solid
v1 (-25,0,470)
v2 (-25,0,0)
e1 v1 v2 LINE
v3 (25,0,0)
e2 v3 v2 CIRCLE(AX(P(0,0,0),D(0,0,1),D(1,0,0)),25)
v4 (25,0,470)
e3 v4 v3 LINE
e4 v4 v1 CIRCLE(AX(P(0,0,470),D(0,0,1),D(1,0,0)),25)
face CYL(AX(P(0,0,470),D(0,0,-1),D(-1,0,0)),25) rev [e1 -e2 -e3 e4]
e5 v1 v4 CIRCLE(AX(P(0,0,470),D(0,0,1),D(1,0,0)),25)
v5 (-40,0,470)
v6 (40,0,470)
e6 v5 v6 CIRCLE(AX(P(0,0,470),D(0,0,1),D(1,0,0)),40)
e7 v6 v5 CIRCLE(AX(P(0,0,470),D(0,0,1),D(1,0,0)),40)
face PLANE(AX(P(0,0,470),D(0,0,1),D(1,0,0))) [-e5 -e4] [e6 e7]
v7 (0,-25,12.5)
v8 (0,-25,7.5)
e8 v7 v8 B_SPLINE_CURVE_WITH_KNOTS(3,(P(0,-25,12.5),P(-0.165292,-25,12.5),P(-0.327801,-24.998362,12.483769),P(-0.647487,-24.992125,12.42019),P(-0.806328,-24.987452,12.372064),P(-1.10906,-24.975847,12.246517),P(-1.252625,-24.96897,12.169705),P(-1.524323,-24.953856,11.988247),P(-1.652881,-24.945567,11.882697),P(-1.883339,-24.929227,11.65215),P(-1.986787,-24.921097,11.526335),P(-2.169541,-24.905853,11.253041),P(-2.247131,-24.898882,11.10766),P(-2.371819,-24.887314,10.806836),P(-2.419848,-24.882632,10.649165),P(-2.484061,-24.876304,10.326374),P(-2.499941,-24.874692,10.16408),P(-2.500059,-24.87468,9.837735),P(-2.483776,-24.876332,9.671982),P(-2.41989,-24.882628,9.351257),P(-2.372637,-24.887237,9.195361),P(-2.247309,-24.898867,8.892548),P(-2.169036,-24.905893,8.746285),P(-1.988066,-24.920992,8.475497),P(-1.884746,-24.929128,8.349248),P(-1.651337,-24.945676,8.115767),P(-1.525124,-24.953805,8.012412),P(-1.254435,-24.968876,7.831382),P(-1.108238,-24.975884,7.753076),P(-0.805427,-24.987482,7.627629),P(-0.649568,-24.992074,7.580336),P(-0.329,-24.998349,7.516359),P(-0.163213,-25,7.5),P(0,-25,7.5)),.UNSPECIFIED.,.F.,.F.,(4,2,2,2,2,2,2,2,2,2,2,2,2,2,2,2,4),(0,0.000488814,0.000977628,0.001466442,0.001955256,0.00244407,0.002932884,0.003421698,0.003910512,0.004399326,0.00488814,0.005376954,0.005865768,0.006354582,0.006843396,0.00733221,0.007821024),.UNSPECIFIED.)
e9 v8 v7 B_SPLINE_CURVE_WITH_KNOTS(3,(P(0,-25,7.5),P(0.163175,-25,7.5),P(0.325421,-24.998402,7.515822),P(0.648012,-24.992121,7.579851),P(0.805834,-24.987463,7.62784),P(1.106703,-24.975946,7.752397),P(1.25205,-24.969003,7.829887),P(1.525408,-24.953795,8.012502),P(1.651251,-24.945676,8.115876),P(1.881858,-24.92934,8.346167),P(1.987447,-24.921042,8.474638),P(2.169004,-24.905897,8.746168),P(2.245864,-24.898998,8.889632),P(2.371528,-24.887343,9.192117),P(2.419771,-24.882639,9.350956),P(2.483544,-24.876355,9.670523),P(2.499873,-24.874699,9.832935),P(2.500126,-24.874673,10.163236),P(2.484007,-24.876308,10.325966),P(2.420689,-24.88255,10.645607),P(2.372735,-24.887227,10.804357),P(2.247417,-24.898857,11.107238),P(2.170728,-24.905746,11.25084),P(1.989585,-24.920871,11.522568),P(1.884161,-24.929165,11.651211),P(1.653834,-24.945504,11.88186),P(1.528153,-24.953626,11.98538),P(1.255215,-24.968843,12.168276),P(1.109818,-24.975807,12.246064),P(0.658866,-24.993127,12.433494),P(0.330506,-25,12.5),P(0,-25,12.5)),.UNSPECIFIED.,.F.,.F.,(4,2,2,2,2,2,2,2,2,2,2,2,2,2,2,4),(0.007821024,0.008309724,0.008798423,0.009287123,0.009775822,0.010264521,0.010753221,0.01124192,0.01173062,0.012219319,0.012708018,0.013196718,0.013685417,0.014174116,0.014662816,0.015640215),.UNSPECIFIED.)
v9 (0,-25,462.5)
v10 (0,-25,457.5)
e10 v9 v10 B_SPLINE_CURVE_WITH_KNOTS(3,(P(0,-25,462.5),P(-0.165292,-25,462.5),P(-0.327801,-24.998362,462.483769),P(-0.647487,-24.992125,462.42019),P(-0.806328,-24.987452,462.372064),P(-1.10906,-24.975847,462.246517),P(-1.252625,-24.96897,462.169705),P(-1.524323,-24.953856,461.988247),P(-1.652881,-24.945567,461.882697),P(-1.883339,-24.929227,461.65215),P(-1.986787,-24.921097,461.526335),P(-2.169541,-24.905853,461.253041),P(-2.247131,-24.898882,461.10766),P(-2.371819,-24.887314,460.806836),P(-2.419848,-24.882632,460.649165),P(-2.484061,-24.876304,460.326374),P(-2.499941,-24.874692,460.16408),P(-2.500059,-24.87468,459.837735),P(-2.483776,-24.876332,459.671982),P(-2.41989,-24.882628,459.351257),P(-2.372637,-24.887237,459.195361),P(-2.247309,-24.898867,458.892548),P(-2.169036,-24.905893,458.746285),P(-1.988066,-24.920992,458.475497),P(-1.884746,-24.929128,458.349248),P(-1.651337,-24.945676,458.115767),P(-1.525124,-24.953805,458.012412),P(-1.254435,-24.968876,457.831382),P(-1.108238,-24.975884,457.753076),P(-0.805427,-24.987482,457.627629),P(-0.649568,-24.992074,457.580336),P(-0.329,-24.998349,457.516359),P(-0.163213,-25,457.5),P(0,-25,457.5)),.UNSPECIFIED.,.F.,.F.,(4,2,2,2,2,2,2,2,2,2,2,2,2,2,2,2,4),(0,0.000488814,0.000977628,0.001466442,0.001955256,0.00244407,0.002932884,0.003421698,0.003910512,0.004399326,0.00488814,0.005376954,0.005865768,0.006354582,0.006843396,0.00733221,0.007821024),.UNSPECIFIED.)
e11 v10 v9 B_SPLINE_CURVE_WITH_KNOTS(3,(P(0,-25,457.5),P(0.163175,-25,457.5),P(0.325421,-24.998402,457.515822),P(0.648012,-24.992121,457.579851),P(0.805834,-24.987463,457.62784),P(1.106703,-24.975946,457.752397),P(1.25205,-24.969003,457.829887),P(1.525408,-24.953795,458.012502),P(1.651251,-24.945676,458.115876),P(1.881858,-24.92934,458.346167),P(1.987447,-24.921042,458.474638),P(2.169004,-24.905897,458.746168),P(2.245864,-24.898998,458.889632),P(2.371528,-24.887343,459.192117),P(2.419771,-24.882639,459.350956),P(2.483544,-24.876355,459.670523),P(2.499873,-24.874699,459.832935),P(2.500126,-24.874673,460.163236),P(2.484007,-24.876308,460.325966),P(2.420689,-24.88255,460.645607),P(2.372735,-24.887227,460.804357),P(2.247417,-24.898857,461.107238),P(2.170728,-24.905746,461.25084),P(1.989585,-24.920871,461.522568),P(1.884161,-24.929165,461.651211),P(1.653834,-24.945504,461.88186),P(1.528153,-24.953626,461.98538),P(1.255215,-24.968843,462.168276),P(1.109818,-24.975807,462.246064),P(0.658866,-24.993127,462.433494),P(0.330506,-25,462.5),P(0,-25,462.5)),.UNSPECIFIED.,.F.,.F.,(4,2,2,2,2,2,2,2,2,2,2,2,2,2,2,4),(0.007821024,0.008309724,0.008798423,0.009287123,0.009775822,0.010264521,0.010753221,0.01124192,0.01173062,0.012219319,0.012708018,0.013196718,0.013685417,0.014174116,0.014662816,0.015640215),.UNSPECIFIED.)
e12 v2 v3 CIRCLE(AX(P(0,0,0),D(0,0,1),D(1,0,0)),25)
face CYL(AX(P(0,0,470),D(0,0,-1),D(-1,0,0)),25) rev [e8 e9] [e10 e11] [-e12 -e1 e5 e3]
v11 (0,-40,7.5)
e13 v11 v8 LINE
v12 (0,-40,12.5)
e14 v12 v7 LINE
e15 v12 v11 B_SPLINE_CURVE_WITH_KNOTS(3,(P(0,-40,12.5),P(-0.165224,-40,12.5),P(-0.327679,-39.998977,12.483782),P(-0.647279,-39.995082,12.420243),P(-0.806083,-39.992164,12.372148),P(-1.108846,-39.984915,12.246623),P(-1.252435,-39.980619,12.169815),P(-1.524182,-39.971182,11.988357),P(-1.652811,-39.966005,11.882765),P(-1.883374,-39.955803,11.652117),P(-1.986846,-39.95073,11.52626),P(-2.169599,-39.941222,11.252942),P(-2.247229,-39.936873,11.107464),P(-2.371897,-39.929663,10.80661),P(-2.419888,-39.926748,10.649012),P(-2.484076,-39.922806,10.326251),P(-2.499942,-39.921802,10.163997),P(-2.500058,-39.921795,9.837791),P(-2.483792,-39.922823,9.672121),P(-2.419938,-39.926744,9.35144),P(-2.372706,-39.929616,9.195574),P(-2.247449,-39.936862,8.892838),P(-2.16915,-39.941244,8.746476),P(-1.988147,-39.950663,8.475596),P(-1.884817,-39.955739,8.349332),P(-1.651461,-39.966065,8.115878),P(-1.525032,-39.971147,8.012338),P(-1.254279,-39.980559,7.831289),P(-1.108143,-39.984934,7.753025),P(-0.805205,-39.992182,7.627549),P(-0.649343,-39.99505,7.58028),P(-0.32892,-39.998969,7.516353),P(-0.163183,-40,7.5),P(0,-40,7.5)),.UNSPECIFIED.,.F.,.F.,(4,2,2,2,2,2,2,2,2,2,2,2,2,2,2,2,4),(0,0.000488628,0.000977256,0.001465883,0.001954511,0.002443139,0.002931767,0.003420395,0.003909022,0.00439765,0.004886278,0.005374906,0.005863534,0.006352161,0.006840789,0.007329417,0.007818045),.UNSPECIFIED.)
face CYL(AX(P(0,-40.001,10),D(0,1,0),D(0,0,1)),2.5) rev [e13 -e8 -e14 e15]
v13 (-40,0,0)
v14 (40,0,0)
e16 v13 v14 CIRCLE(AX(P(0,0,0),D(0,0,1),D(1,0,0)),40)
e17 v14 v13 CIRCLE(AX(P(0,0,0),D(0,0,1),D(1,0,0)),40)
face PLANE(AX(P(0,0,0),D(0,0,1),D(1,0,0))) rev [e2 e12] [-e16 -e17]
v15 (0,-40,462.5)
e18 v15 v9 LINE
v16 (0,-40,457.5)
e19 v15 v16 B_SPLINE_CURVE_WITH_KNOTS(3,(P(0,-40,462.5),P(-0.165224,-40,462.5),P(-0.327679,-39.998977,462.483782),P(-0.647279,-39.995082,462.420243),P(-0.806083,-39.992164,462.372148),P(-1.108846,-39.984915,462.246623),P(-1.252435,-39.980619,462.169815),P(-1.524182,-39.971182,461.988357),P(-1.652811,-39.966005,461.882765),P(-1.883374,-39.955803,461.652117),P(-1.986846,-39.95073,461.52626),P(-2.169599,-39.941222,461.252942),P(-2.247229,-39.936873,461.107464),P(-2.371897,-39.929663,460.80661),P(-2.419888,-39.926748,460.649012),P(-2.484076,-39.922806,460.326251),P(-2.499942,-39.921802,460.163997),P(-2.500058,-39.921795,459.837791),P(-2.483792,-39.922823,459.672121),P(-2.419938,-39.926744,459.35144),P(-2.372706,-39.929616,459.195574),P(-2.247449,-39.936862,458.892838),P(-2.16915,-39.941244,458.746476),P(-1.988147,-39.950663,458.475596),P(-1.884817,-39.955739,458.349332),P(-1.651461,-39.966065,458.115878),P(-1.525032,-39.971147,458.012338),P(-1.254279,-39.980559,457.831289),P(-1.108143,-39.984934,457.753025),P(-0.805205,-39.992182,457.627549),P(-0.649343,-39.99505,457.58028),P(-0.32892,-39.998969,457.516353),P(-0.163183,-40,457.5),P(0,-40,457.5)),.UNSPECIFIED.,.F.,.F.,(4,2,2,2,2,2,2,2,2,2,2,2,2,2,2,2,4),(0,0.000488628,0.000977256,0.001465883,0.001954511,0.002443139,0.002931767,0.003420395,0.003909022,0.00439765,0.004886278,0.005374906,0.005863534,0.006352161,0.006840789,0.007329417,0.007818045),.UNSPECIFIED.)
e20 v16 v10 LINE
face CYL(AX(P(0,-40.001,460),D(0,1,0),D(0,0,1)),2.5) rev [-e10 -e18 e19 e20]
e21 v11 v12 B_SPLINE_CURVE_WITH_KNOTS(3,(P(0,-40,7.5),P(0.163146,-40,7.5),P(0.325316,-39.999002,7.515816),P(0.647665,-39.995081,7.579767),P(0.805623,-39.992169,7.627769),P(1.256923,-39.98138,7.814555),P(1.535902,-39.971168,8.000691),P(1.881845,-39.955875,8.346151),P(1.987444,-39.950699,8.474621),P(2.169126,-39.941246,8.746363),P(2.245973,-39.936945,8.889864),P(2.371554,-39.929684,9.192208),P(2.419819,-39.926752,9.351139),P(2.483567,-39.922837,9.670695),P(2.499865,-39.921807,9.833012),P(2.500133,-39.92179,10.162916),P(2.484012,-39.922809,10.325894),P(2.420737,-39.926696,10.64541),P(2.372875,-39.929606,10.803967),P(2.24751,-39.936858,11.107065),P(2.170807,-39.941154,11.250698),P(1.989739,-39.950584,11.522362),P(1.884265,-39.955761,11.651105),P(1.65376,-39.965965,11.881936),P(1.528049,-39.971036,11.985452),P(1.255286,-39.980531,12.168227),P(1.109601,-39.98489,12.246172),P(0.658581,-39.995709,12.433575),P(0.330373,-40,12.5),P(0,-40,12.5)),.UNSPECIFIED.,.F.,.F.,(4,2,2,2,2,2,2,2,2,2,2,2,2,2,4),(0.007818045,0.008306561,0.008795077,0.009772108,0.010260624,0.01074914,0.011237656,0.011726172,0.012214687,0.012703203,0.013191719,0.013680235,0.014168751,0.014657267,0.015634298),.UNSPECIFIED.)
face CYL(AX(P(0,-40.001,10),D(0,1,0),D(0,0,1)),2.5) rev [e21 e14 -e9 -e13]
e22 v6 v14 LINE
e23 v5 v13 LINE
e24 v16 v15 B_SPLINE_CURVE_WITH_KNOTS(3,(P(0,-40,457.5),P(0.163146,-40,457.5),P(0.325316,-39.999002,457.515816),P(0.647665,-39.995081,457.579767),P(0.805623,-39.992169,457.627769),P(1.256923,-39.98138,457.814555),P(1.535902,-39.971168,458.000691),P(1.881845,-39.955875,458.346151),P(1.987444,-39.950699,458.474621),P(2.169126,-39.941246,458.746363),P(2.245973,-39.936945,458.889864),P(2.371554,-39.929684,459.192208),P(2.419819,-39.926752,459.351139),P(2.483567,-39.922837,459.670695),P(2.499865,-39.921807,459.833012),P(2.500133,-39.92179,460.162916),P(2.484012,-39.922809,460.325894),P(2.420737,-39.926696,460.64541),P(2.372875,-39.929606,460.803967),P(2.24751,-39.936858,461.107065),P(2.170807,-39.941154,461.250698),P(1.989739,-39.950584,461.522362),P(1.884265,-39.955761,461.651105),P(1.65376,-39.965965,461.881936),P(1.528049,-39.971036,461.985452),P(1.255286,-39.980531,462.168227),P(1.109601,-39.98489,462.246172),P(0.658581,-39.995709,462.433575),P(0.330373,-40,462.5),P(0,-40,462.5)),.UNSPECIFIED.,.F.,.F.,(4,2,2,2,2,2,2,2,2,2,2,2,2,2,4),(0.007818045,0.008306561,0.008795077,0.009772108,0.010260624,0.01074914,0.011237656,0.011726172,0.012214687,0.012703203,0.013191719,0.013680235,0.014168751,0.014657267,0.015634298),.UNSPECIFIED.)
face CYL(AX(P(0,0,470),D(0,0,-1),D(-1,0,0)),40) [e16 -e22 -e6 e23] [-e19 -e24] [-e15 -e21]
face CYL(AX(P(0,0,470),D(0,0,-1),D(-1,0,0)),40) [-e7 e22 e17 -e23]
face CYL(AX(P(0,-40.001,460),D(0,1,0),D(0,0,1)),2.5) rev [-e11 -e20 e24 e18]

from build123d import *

# Parameters (mm, degrees)
SKETCH1_R               = 40
SKETCH1_R_2             = 25
BOSS_EXTRUDE1_DEPTH     = 470
CUT_EXTRUDE1_REACH      = 475.392
CUT_EXTRUDE1_END_RADIUS = 40
SKETCH2_R               = 2.5


with BuildPart() as part:
    # Sketch1 → Boss-Extrude1 (new body)
    with BuildSketch(Plane.XY):
        with Locations(Location((0, 0, 0), (0, 0, 180))):
            Circle(SKETCH1_R)
        with Locations(Location((0, 0, 0), (0, 0, 180))):
            Circle(SKETCH1_R_2, mode=Mode.SUBTRACT)
    extrude(amount=BOSS_EXTRUDE1_DEPTH)

    # Cut-Extrude1: up to this cylinder (the profile starts inside it)
    cut_extrude1_end = Plane(origin=(0, 0, 235), z_dir=(0, 0, -1)) * Cylinder(CUT_EXTRUDE1_END_RADIUS, 1481.784, mode=Mode.PRIVATE)
    # Sketch2 → Cut-Extrude1 (cut, up to the surface)
    with BuildSketch(Plane(origin=(0, 0, 0), x_dir=(1, 0, 0), z_dir=(0, 1, 0)), mode=Mode.PRIVATE) as cut_extrude1_sk1:
        with Locations(Location((0, -460, 0), (0, 0, 270))):
            Circle(SKETCH2_R)
    cut_extrude1_tool1 = extrude(cut_extrude1_sk1.sketch, amount=-CUT_EXTRUDE1_REACH, mode=Mode.PRIVATE) & cut_extrude1_end
    add(cut_extrude1_tool1.solids().sort_by_distance((0, 0, 460))[0], mode=Mode.SUBTRACT)
    # Sketch2 → Cut-Extrude1 (cut, up to the surface)
    with BuildSketch(Plane(origin=(0, 0, 0), x_dir=(1, 0, 0), z_dir=(0, 1, 0)), mode=Mode.PRIVATE) as cut_extrude1_sk2:
        with Locations(Location((0, -10, 0), (0, 0, 270))):
            Circle(SKETCH2_R)
    cut_extrude1_tool2 = extrude(cut_extrude1_sk2.sketch, amount=-CUT_EXTRUDE1_REACH, mode=Mode.PRIVATE) & cut_extrude1_end
    add(cut_extrude1_tool2.solids().sort_by_distance((0, 0, 10))[0], mode=Mode.SUBTRACT)


solid = part.part
